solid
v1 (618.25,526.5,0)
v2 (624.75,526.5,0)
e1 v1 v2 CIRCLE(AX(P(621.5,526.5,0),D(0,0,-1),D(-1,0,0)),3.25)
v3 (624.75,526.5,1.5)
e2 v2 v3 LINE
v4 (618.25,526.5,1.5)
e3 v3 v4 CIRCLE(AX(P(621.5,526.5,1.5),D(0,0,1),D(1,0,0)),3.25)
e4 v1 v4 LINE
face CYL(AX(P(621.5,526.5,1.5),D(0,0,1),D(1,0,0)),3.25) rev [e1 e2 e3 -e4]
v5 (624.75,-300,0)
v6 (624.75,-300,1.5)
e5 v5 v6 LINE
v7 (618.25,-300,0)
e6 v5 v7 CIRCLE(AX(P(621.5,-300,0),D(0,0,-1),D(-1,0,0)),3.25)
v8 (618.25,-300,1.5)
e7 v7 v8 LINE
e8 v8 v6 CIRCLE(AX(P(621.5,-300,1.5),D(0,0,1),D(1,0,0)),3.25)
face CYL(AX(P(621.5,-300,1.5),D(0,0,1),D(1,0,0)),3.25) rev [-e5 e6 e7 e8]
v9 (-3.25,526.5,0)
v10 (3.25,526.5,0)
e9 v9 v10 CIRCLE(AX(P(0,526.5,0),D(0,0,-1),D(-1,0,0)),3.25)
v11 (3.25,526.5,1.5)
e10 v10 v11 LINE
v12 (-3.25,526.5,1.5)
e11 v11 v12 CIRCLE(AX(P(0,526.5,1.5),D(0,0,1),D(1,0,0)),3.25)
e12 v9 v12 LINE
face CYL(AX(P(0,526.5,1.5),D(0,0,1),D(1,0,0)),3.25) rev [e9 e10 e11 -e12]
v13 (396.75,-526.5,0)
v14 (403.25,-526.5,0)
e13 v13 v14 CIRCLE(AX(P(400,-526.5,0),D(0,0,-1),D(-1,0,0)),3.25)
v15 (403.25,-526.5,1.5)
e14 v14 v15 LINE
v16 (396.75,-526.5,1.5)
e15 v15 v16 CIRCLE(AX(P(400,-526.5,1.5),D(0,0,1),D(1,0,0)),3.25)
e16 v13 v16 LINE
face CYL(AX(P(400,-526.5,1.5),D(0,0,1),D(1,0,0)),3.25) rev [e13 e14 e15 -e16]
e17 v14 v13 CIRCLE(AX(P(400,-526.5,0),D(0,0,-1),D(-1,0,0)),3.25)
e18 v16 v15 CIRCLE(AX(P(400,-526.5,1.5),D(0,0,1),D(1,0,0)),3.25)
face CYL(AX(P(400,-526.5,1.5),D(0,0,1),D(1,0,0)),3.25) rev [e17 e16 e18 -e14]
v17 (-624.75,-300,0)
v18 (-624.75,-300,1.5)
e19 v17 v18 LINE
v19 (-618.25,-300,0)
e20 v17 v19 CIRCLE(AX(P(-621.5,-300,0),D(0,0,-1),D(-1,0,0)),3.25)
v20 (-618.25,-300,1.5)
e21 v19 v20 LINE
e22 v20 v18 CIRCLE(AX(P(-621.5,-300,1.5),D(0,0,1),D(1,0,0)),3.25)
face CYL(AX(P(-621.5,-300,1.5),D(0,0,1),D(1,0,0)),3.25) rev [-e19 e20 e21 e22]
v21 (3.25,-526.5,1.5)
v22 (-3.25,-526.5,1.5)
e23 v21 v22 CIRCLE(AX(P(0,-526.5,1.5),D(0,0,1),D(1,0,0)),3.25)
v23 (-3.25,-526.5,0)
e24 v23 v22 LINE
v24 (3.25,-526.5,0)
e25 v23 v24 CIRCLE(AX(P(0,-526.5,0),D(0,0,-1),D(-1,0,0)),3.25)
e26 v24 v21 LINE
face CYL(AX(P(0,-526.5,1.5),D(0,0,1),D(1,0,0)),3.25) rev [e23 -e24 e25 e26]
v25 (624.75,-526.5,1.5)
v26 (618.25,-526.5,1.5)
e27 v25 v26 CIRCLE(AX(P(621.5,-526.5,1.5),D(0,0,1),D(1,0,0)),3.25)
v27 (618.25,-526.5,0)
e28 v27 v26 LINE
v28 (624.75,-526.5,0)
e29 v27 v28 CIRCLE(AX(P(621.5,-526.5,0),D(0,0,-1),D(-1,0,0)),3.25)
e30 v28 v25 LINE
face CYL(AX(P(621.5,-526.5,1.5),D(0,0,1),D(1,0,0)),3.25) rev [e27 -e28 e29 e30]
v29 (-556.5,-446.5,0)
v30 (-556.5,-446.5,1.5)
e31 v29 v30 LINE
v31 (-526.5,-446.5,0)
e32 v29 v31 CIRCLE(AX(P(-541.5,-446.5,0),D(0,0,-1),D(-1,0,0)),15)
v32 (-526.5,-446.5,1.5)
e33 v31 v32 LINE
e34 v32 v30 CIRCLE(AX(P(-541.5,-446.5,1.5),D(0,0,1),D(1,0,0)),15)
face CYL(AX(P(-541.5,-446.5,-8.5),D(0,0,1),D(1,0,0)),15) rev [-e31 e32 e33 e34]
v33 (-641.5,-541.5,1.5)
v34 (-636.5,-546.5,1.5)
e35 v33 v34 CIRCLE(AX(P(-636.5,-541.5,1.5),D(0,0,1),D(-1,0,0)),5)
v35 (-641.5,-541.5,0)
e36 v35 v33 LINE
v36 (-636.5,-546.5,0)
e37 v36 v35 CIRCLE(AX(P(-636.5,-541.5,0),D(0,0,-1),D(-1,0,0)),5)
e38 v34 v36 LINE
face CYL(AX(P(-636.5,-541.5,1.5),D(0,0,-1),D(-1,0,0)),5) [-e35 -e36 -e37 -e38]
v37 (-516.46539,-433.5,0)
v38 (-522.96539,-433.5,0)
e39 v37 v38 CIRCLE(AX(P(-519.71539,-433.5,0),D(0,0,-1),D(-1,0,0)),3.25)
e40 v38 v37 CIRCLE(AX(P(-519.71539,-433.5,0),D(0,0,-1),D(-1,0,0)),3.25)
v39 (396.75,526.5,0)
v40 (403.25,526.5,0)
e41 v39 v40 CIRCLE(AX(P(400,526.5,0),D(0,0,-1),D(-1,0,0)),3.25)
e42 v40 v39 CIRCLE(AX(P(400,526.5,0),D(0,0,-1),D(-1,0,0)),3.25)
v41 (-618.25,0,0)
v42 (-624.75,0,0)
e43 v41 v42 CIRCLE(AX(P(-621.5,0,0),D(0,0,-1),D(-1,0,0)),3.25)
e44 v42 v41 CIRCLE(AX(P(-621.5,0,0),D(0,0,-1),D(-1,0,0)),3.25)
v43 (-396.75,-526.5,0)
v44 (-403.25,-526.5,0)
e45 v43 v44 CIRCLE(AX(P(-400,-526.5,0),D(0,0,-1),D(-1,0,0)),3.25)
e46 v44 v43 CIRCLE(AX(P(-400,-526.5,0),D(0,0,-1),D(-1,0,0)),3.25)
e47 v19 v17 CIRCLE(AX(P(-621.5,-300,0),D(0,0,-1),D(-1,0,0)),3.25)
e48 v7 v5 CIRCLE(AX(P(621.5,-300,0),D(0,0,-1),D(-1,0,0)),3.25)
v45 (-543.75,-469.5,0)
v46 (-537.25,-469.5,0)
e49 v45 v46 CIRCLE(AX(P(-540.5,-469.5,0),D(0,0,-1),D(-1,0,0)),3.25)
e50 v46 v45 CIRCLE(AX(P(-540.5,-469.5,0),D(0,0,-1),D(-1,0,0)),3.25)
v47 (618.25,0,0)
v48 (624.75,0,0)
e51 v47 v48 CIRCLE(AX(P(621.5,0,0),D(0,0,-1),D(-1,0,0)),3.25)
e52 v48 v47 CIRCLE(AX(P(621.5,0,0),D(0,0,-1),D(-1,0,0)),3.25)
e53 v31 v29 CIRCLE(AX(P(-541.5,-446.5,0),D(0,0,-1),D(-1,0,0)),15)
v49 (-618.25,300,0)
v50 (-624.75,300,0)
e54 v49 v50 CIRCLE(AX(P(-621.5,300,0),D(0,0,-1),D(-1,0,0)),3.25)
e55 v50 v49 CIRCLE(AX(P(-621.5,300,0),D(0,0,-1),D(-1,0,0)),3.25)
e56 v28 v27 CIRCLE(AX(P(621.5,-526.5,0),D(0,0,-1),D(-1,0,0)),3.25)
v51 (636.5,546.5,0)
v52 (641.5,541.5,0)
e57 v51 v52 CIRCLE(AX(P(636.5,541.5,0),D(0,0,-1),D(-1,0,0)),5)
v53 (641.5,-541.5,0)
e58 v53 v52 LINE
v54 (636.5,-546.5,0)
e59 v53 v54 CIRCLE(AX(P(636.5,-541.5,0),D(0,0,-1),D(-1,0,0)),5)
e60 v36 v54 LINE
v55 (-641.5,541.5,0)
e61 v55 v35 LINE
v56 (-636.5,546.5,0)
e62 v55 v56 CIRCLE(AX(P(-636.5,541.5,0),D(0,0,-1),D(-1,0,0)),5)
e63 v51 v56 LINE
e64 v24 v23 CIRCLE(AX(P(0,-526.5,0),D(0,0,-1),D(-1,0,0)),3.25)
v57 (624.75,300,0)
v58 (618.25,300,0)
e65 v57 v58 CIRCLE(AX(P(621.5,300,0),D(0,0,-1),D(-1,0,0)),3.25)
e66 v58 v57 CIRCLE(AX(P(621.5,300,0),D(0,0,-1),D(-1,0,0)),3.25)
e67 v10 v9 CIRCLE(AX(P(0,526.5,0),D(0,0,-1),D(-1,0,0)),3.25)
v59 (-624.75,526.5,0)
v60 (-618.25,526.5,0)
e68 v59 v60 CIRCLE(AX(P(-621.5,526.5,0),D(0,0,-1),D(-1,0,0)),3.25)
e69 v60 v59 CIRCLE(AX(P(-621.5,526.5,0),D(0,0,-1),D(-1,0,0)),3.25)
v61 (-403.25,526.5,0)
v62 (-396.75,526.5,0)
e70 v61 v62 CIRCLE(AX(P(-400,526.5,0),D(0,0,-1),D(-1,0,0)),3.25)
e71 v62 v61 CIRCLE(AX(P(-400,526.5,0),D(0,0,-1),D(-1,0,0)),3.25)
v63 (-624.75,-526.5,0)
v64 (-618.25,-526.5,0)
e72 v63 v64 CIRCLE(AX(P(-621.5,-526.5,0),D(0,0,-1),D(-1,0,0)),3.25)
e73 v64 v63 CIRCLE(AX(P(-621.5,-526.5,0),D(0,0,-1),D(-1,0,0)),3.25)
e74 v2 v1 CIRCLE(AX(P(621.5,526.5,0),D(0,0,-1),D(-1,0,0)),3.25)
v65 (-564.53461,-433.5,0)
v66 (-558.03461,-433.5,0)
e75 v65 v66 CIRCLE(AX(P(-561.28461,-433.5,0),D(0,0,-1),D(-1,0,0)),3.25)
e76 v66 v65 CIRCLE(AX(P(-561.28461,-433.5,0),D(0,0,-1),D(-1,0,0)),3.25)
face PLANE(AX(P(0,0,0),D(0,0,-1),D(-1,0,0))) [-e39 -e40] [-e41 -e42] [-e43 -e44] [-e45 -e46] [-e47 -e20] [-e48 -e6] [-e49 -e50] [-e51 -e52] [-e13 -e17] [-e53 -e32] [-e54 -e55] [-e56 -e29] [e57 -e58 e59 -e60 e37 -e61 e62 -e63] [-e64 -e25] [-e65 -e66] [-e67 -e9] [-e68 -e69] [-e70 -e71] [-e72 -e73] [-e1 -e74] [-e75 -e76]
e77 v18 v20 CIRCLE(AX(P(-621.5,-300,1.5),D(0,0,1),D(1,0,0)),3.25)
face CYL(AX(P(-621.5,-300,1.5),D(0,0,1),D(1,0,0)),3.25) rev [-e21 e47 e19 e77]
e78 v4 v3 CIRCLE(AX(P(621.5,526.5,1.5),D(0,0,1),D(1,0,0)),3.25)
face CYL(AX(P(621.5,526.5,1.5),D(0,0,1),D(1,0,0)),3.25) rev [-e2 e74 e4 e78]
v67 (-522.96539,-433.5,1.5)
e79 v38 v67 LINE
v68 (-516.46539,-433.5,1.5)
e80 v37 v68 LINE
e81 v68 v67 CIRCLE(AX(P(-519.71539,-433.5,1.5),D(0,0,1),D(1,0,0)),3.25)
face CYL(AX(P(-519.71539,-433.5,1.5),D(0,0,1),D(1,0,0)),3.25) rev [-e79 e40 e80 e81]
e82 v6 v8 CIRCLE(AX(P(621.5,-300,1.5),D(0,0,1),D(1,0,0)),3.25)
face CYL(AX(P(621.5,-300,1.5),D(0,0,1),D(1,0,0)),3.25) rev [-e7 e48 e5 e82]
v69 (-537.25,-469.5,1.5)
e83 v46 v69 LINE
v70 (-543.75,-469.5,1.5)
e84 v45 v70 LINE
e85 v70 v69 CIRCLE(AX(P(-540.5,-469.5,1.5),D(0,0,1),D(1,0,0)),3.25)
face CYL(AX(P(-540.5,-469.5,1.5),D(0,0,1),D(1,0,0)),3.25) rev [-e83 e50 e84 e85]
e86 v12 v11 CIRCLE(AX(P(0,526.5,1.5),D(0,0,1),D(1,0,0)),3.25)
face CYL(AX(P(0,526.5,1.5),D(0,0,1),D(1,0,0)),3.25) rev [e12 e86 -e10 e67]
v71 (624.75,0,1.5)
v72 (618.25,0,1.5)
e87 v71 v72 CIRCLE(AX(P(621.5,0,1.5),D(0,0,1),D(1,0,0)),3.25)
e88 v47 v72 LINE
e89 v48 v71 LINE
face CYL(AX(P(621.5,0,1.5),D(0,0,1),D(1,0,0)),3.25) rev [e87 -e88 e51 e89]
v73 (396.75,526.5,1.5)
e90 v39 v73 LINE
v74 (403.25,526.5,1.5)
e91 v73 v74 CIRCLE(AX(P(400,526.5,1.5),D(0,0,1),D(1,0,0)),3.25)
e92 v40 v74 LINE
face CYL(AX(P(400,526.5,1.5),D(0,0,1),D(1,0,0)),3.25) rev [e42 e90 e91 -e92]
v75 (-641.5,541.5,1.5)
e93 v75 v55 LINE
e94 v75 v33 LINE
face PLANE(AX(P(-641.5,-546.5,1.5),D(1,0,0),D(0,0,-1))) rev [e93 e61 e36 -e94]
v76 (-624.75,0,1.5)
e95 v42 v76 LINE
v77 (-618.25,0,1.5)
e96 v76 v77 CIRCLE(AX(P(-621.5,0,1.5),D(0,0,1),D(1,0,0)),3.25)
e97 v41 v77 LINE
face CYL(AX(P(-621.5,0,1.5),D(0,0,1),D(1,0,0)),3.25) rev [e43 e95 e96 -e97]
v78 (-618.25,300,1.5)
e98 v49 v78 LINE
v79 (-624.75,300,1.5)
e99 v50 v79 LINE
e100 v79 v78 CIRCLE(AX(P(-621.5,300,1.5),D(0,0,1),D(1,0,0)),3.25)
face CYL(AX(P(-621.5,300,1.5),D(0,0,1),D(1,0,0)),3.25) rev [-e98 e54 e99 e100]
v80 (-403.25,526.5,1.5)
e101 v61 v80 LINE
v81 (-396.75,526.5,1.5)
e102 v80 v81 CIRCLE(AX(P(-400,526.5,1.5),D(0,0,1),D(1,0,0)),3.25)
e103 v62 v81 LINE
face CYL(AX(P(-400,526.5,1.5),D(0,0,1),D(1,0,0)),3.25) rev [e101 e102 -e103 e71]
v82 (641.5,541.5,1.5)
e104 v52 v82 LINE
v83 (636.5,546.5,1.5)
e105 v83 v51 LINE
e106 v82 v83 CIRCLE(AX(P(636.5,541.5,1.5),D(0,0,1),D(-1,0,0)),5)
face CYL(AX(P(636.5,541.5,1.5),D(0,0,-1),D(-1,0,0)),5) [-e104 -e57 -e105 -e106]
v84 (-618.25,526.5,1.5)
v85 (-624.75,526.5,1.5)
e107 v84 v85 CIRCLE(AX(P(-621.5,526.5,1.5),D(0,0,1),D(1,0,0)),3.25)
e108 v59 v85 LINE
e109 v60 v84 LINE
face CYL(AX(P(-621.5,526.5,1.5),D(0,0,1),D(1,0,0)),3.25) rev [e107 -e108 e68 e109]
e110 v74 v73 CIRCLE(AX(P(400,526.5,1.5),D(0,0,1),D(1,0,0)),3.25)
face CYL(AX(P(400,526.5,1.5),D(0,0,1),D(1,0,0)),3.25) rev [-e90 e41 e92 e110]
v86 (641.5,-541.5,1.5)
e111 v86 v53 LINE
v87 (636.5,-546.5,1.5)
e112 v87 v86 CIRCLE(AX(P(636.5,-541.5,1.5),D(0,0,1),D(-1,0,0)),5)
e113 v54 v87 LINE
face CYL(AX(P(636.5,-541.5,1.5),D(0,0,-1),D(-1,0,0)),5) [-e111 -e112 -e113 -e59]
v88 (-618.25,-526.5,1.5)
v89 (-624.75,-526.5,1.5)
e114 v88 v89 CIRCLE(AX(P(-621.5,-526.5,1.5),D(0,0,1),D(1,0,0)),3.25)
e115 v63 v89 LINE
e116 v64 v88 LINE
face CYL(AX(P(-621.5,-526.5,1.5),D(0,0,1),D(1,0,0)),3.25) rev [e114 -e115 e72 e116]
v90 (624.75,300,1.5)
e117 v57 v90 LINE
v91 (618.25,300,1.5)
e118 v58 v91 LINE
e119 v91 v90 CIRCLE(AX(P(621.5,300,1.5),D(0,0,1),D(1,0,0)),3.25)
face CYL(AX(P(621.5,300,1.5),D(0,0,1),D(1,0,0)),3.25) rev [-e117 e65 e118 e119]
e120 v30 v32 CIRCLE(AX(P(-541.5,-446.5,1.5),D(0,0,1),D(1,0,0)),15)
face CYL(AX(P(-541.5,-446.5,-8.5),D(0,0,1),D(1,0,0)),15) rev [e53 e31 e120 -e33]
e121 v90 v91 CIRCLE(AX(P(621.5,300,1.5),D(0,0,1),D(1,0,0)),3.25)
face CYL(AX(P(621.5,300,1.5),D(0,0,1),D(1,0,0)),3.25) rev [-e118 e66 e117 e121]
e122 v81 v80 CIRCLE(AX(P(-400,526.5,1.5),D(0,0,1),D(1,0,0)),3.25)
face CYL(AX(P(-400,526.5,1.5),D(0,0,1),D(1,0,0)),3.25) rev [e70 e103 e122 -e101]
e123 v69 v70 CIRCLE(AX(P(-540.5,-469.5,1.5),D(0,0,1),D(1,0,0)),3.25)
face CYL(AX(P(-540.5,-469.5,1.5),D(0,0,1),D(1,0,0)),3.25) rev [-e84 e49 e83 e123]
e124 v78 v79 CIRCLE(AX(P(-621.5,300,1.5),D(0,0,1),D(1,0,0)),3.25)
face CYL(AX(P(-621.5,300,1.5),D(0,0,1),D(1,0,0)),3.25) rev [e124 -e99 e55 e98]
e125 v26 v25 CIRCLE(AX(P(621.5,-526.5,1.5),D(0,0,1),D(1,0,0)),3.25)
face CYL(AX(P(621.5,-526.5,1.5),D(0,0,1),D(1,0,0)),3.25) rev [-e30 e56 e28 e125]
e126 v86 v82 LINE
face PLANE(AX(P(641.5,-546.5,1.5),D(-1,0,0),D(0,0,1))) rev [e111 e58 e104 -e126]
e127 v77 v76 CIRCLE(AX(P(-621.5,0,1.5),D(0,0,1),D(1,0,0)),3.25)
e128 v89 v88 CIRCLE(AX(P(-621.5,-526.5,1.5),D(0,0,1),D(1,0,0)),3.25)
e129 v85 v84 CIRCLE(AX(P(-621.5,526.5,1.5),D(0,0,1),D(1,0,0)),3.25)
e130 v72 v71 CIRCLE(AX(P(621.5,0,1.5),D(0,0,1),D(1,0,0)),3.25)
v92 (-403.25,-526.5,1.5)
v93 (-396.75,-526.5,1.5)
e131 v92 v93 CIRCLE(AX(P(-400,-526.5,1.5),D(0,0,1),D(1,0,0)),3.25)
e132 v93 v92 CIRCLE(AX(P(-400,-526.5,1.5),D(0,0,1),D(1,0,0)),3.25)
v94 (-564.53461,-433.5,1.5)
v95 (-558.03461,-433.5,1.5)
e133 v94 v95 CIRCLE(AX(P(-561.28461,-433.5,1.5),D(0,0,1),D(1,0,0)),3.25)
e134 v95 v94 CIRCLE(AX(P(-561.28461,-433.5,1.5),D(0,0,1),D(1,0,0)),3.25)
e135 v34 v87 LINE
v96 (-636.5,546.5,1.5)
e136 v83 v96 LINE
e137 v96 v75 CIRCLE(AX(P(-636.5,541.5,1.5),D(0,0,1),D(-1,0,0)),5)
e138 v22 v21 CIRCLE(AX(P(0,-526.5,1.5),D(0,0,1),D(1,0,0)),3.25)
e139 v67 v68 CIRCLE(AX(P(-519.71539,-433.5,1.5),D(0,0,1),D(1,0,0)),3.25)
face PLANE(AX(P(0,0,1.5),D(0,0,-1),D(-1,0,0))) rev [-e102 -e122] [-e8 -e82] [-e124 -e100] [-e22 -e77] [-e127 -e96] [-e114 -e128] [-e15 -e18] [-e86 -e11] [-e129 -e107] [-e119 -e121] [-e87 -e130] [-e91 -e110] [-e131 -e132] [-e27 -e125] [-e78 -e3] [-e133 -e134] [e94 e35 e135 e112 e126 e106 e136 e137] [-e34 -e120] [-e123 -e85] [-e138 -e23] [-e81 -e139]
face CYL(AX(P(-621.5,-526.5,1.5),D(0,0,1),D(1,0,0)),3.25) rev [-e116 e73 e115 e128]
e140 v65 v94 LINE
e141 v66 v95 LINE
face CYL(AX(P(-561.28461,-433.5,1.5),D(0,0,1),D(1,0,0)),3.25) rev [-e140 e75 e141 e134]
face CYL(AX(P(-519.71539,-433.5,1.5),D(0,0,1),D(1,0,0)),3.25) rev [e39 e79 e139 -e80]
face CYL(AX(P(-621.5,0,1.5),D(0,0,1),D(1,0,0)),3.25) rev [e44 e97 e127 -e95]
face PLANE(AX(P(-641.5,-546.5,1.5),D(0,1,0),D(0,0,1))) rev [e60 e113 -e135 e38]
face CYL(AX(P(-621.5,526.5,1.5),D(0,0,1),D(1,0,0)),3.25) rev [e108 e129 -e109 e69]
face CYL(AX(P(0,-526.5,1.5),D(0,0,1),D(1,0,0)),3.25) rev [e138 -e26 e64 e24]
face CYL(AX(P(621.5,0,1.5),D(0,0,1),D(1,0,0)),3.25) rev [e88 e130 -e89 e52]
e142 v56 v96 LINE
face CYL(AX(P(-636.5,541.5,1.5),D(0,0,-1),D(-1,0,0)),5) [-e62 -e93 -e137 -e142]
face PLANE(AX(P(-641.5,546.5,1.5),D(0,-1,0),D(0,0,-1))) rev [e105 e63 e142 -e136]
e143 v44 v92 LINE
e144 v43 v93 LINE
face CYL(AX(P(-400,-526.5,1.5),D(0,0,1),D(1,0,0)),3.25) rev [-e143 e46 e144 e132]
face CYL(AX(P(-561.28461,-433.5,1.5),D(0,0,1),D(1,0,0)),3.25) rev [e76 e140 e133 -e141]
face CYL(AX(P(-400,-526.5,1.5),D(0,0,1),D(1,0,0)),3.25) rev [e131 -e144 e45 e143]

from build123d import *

# Parameters (mm, degrees)
SKETCH_1_W                  = 1283
SKETCH_1_H                  = 1093
EXTRUDE_1_DEPTH             = 1.5
FILLET_1_R                  = 5
HOLE_WIZARD_6_5_6_5_1_D     = 6.5
HOLE_WIZARD_6_5_6_5_1_DEPTH = 15.61
HOLE_WIZARD_6_5_6_5_1_TIP   = 1.876388375
SKETCH_5_R                  = 15
CUT_EXTRUDE_1_DEPTH         = 10
HOLE_WIZARD_6_5_6_5_2_D     = 6.5
HOLE_WIZARD_6_5_6_5_2_DEPTH = 15.61
HOLE_WIZARD_6_5_6_5_2_TIP   = 1.876388375


with BuildPart() as part:
    # 草图1 → 凸台-拉伸1 (new body)
    with BuildSketch(Plane.XY):
        Rectangle(SKETCH_1_W, SKETCH_1_H)
    extrude(amount=EXTRUDE_1_DEPTH)

    # 圆角1
    fillet_1_edges = [part.edges().sort_by_distance(p)[0] for p in [
        (-641.5, 546.5, 0.75),
        (641.5, 546.5, 0.75),
        (641.5, -546.5, 0.75),
        (-641.5, -546.5, 0.75),
    ]]
    fillet(fillet_1_edges, radius=FILLET_1_R)

    # Ø6.5 (6.5) 直径孔1
    with Locations(Plane.XY.offset(1.5)):
        with Locations((0, 526.5), (400, 526.5), (-400, 526.5), (-621.5, 300), (-621.5, 0), (-621.5, -300), (-400, -526.5), (0, -526.5), (400, -526.5), (621.5, 300), (621.5, 0), (621.5, -300), (-621.5, 526.5), (-621.5, -526.5), (621.5, -526.5), (621.5, 526.5)):
            Hole(HOLE_WIZARD_6_5_6_5_1_D / 2, depth=HOLE_WIZARD_6_5_6_5_1_DEPTH)
            with Locations((0, 0, -(HOLE_WIZARD_6_5_6_5_1_DEPTH + HOLE_WIZARD_6_5_6_5_1_TIP / 2))):  # 120° drill point
                Cone(0, HOLE_WIZARD_6_5_6_5_1_D / 2, HOLE_WIZARD_6_5_6_5_1_TIP, mode=Mode.SUBTRACT)

    # 草图5 → 切除-拉伸1 (cut)
    with BuildSketch(Plane.XY.offset(1.5)):
        with Locations((-541.5, -446.5)):
            Circle(SKETCH_5_R)
    extrude(amount=-CUT_EXTRUDE_1_DEPTH, mode=Mode.SUBTRACT)

    # Ø6.5 (6.5) 直径孔2
    with Locations(Plane.XY.offset(1.5)):
        with Locations((-561.284609691, -433.5), (-540.5, -469.5), (-519.715390309, -433.5)):
            Hole(HOLE_WIZARD_6_5_6_5_2_D / 2, depth=HOLE_WIZARD_6_5_6_5_2_DEPTH)
            with Locations((0, 0, -(HOLE_WIZARD_6_5_6_5_2_DEPTH + HOLE_WIZARD_6_5_6_5_2_TIP / 2))):  # 120° drill point
                Cone(0, HOLE_WIZARD_6_5_6_5_2_D / 2, HOLE_WIZARD_6_5_6_5_2_TIP, mode=Mode.SUBTRACT)


solid = part.part
